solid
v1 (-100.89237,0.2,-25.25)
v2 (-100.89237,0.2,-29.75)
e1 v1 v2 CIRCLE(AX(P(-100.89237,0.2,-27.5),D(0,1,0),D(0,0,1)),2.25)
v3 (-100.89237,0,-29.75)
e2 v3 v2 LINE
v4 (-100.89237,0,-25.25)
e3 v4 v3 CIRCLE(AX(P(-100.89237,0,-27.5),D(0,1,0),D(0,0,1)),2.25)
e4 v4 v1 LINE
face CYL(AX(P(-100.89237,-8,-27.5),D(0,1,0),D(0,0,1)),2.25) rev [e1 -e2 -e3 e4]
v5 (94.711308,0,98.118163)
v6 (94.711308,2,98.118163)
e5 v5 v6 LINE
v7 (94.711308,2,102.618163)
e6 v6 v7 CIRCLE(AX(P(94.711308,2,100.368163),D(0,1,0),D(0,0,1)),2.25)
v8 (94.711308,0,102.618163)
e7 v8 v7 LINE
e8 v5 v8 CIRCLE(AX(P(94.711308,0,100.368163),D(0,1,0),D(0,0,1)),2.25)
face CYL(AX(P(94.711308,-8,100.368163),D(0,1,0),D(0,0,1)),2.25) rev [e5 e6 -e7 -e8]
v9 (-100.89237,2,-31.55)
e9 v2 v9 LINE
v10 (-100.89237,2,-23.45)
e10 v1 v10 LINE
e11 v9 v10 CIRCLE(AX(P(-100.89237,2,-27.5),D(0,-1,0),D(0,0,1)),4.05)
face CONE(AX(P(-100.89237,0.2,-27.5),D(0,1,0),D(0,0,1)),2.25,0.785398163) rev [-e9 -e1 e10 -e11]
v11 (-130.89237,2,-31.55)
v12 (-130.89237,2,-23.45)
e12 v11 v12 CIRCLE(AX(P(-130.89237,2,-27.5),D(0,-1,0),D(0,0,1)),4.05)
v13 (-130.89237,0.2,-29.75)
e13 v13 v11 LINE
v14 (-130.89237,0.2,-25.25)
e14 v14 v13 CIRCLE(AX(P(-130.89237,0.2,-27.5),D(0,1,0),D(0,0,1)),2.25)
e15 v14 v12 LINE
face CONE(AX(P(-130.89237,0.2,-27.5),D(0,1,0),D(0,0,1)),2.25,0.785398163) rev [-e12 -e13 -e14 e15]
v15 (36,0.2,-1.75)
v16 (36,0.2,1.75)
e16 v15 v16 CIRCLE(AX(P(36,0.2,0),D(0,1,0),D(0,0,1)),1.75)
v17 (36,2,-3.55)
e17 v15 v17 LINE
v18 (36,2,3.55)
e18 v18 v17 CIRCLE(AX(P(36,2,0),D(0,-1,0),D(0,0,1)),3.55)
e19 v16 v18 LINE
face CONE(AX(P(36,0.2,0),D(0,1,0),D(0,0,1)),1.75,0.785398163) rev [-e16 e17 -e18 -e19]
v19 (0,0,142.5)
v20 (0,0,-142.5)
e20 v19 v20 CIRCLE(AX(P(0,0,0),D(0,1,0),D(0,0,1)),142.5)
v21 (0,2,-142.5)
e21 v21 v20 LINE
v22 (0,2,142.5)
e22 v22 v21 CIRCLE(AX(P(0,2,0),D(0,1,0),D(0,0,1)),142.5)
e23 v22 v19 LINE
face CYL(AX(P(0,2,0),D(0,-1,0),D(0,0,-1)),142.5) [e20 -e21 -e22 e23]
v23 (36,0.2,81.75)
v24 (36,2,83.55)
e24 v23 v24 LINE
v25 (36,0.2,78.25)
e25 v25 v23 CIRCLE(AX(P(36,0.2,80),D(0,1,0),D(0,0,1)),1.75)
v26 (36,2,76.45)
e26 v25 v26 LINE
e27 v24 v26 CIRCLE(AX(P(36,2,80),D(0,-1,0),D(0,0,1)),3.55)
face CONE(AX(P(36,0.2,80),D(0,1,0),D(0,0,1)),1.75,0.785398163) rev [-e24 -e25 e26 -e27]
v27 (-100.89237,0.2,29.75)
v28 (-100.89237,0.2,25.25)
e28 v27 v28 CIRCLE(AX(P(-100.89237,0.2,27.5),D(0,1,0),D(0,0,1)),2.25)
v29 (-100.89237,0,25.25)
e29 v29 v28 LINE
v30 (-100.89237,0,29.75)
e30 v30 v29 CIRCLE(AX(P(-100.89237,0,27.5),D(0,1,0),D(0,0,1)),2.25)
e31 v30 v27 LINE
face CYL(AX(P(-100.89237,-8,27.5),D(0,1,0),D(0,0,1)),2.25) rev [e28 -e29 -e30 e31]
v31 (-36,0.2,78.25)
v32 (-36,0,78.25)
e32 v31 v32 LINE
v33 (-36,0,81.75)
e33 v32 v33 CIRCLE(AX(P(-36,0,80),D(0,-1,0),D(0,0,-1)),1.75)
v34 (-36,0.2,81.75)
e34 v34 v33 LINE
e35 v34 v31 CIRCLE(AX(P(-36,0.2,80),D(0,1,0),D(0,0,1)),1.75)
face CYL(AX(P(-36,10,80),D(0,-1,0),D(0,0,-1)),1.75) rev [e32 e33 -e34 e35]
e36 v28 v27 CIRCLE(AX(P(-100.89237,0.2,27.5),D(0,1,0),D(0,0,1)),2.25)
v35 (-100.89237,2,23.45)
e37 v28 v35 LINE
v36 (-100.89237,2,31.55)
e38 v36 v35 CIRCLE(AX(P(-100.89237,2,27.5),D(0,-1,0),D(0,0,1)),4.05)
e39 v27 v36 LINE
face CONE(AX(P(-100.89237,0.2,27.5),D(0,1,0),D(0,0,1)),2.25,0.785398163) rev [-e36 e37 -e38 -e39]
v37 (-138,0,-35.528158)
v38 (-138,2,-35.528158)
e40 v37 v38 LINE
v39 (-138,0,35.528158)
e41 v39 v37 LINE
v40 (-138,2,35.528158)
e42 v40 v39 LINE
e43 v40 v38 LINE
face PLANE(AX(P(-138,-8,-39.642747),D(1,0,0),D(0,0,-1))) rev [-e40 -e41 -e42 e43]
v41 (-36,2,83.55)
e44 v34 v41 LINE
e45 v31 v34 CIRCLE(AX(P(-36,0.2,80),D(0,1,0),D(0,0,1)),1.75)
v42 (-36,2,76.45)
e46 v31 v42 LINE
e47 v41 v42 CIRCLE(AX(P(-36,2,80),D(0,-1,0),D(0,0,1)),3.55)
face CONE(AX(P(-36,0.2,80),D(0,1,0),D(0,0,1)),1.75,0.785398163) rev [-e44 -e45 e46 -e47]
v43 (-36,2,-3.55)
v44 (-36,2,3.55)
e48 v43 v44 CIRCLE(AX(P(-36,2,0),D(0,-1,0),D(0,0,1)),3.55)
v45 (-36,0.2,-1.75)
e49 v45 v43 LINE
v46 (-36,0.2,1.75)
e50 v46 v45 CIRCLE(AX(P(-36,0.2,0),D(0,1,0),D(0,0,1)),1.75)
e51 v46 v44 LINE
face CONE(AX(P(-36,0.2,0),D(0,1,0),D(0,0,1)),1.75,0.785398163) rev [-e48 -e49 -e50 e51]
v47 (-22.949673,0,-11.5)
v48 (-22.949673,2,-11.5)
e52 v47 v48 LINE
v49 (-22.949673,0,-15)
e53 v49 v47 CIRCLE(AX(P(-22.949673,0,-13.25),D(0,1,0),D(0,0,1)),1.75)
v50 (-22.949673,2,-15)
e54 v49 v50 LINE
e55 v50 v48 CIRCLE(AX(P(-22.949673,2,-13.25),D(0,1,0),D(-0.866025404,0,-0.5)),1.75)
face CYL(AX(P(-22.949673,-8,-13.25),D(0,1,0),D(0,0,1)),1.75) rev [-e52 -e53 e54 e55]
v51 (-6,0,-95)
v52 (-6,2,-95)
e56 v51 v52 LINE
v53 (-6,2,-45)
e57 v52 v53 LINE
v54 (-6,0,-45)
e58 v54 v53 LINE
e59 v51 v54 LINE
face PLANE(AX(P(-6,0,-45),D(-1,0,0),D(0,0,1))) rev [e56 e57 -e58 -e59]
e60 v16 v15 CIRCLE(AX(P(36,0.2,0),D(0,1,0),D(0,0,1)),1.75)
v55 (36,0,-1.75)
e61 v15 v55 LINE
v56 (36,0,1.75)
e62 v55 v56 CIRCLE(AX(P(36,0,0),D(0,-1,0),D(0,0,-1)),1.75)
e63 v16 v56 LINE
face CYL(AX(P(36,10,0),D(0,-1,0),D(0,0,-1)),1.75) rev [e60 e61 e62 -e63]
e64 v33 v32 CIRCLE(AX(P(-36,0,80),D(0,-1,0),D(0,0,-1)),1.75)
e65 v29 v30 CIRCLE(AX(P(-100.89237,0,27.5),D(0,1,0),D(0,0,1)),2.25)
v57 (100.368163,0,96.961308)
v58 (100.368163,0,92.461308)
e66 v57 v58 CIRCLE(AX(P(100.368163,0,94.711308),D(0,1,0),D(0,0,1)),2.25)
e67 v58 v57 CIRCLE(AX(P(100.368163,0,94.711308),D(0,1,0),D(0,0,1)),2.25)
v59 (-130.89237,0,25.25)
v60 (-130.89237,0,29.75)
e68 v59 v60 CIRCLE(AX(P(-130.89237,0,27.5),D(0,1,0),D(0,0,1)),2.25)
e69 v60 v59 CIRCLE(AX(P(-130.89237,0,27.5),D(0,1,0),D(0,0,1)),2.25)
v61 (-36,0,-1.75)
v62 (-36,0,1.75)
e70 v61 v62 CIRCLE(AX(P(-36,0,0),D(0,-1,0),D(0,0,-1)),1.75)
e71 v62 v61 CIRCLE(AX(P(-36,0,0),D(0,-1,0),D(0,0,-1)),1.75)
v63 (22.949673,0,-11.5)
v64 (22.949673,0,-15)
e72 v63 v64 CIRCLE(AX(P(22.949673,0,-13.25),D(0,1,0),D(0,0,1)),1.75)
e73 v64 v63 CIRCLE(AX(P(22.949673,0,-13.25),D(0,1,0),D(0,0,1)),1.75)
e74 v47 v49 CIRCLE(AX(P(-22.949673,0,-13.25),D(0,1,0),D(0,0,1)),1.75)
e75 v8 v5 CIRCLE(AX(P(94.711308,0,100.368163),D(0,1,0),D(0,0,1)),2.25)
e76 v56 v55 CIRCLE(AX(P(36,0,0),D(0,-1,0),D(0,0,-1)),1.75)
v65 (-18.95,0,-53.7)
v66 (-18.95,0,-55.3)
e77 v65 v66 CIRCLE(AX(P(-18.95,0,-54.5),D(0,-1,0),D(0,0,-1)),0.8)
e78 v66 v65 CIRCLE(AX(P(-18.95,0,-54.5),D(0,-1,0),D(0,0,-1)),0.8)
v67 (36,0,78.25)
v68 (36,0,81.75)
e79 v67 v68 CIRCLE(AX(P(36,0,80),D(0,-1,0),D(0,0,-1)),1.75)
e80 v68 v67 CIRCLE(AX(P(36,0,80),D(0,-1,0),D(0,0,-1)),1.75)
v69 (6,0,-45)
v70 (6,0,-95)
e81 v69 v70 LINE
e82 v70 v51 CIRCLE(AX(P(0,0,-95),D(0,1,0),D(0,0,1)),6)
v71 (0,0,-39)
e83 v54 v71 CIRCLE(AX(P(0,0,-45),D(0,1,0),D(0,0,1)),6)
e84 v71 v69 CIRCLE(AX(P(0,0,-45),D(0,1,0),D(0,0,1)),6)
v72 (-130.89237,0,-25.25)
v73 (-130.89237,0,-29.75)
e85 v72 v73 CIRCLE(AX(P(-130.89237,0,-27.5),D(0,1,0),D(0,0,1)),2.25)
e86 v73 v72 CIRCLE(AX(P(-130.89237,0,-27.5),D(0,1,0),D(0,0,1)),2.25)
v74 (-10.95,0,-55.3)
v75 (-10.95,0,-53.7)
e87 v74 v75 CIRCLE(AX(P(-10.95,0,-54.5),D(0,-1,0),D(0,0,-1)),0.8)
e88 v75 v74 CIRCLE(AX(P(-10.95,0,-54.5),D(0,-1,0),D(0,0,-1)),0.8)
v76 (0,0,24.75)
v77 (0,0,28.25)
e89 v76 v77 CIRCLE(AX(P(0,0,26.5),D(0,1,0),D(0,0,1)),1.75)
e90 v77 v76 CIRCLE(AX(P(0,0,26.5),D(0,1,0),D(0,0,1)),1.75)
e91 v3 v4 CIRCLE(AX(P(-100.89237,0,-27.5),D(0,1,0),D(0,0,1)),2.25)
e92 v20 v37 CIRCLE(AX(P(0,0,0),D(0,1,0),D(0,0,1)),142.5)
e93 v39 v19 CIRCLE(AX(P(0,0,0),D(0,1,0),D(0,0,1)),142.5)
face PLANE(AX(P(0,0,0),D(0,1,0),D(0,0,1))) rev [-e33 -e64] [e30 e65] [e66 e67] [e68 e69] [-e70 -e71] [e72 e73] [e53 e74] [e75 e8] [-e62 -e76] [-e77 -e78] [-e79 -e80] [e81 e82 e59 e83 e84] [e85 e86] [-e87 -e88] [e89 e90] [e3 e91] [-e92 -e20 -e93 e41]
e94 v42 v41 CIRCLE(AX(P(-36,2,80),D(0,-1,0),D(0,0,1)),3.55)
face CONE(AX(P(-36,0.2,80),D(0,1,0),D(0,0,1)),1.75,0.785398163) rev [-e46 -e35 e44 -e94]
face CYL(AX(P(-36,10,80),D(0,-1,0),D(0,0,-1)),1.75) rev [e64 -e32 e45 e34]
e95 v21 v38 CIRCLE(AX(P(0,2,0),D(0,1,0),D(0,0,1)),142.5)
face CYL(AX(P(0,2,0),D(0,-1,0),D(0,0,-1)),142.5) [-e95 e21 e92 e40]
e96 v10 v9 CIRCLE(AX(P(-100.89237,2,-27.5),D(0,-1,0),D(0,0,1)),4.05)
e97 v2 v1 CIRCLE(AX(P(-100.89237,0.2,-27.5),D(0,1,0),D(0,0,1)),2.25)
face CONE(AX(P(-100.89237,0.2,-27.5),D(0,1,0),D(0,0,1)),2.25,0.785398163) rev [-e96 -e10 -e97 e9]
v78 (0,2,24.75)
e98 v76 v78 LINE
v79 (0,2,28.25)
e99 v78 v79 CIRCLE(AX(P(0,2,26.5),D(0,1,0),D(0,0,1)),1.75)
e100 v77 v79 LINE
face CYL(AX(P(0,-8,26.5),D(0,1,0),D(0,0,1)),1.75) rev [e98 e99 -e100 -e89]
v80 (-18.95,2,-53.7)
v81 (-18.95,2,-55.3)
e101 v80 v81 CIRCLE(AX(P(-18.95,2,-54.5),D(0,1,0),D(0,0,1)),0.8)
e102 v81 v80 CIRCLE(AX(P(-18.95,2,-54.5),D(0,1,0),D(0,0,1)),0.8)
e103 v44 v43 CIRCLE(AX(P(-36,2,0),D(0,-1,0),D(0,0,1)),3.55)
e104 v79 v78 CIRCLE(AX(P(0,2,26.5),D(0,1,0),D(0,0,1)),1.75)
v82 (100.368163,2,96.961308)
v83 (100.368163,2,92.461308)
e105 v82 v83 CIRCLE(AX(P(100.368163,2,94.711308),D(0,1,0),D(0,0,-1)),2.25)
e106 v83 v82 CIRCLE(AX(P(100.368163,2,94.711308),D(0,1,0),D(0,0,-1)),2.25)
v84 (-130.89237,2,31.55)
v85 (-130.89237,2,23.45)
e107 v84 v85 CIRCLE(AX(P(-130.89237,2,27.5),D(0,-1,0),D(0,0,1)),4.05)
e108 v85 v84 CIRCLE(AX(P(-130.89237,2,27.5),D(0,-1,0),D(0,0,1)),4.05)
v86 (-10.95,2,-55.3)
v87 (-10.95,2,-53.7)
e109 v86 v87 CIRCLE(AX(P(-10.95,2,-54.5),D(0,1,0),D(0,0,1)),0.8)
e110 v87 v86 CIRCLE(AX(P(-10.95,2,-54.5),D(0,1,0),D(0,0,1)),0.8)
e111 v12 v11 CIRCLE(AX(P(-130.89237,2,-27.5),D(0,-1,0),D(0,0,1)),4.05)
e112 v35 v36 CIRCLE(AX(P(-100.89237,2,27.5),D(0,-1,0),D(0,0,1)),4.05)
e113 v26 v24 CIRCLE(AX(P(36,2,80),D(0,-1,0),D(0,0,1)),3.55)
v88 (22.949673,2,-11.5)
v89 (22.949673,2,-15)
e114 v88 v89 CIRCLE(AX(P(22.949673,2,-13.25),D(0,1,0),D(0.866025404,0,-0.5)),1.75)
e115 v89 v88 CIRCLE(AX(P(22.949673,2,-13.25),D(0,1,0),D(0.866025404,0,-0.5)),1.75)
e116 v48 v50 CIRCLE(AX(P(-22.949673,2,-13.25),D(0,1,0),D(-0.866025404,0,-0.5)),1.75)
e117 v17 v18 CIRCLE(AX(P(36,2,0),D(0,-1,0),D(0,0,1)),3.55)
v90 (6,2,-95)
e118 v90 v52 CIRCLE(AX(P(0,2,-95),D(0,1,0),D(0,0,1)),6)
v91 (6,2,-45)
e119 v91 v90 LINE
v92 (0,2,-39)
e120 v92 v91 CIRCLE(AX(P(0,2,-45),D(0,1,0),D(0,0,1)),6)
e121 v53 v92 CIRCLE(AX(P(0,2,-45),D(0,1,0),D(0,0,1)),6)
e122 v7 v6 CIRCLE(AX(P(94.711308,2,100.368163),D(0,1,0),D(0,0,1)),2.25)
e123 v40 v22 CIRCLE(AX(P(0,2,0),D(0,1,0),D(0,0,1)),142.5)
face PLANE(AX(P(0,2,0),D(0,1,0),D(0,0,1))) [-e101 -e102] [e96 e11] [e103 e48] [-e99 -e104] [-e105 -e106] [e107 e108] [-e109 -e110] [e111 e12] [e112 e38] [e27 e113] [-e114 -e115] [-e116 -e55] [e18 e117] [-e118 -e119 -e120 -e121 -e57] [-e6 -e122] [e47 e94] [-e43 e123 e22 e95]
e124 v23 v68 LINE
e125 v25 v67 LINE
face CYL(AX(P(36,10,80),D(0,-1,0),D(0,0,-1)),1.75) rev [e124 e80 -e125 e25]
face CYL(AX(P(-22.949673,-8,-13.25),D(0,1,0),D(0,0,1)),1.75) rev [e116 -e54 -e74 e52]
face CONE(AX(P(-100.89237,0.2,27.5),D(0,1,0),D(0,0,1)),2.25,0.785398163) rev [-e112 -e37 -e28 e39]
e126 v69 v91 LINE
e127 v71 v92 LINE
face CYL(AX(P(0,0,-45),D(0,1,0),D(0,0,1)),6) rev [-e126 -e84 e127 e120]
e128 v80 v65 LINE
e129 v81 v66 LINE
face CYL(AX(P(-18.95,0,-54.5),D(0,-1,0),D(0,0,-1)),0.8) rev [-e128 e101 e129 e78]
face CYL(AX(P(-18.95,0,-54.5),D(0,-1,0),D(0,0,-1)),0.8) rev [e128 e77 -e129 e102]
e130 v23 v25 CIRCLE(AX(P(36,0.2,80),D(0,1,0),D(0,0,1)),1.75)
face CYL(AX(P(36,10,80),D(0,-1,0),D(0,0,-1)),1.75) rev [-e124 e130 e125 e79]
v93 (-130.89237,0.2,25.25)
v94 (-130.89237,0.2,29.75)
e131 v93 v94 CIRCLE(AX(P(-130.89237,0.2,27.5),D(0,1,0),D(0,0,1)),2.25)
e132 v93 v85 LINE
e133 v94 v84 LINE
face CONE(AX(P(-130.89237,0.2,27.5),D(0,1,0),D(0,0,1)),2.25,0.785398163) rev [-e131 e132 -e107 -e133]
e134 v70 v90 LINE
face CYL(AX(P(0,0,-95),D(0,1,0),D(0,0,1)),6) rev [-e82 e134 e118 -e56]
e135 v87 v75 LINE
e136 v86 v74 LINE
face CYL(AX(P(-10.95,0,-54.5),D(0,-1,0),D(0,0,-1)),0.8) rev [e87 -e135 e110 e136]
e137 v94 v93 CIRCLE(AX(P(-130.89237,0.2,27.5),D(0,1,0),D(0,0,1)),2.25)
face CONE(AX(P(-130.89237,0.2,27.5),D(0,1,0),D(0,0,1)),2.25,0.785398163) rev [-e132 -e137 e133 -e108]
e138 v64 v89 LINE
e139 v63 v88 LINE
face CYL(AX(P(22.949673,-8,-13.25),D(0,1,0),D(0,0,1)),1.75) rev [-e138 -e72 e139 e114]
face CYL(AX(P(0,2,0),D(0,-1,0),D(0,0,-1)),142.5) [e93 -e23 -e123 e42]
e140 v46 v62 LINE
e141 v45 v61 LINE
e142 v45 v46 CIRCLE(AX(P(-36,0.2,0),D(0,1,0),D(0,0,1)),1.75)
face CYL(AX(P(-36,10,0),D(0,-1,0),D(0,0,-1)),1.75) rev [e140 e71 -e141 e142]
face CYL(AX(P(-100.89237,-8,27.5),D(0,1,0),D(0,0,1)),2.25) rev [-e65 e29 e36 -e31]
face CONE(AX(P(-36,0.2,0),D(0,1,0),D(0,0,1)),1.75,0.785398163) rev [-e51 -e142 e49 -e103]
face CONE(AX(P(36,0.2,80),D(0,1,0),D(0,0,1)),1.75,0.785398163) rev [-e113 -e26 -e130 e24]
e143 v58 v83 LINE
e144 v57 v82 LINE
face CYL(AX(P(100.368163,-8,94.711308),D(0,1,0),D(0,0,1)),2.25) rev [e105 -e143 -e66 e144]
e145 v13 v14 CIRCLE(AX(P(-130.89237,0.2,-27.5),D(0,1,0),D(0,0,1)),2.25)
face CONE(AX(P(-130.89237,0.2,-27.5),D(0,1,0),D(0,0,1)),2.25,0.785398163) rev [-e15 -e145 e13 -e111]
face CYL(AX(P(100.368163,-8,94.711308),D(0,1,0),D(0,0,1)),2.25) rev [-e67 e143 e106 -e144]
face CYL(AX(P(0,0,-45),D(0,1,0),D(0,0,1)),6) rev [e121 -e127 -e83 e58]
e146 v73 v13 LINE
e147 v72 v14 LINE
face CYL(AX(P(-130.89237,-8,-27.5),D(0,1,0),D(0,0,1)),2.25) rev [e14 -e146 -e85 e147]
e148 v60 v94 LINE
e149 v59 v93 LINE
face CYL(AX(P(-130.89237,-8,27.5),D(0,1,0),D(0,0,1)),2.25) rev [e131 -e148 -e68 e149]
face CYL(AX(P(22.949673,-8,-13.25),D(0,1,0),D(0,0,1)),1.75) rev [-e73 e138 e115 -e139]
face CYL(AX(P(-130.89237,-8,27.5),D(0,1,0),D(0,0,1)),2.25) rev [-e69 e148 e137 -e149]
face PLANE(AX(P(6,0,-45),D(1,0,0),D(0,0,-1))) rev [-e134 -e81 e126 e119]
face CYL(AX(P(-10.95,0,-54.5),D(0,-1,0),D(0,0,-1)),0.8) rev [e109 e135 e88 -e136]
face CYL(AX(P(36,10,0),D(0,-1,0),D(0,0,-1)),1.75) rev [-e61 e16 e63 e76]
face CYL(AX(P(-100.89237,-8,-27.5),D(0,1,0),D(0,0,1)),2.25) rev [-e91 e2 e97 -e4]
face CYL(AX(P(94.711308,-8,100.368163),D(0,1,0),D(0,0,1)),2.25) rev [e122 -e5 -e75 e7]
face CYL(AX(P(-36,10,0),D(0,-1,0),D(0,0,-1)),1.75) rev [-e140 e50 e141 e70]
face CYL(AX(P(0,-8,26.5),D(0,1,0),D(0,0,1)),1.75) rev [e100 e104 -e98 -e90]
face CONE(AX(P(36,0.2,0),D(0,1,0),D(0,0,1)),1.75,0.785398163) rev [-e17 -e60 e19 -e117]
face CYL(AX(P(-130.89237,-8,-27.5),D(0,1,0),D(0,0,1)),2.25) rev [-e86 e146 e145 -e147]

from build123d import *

# Parameters (mm, degrees)
SKETCH1_R             = 142.5
BOSS_EXTRUDE1_DEPTH   = 2
SKETCH3_R             = 1.75
CUT_EXTRUDE1_DEPTH    = 10
CIRPATTERN1_COUNT     = 3
SKETCH5_R             = 2.25
CUT_EXTRUDE2_DEPTH    = 10
CUT_EXTRUDE3_DEPTH    = 202.5353567
SKETCH7_R             = 1.75
CUT_EXTRUDE4_DEPTH    = 10
CHAMFER1_SIZE         = 1.8
CHAMFER2_SIZE         = 1.8
M2_TAPPED_HOLE1_D     = 1.6
M2_TAPPED_HOLE1_DEPTH = 5.2
M2_TAPPED_HOLE1_TIP   = 0.480688495
SKETCH9_W             = 15.607073654
SKETCH9_H             = 79.285494628
CUT_EXTRUDE5_DEPTH    = 10


with BuildPart() as part:
    # Sketch1 → Boss-Extrude1 (new body)
    with BuildSketch(Plane(origin=(0, 0, 0), x_dir=(1, 0, 0), z_dir=(0, 1, 0))):
        with Locations(Location((0, 0, 0), (0, 0, 270))):
            Circle(SKETCH1_R)
    extrude(amount=BOSS_EXTRUDE1_DEPTH)

    # Sketch3 → Cut-Extrude1 (cut)
    with BuildSketch(Plane(origin=(0, 2, 0), x_dir=(1, 0, 0), z_dir=(0, 1, 0))):
        with Locations(Location((0, -26.5, 0), (0, 0, 270))):
            Circle(SKETCH3_R)
    cut_extrude1 = extrude(amount=-CUT_EXTRUDE1_DEPTH, mode=Mode.SUBTRACT)

    # CirPattern1: Cut-Extrude1 ×3 about axis
    cirpattern1_axis = Axis((0, 0, 0), (0, 1, 0))
    for i in range(1, CIRPATTERN1_COUNT):
        add(cut_extrude1.rotate(cirpattern1_axis, i * 360 / CIRPATTERN1_COUNT), mode=Mode.SUBTRACT)

    # Sketch5 → Cut-Extrude2 (cut)
    with BuildSketch(Plane(origin=(0, 2, 0), x_dir=(1, 0, 0), z_dir=(0, 1, 0))):
        with Locations(Location((94.711308368, -100.368162618, 0), (0, 0, 270))):
            Circle(SKETCH5_R)
        with Locations(Location((100.368162618, -94.711308368, 0), (0, 0, 270))):
            Circle(SKETCH5_R)
        with Locations(Location((-130.892369907, 27.5, 0), (0, 0, 270))):
            Circle(SKETCH5_R)
        with Locations(Location((-130.892369907, -27.5, 0), (0, 0, 270))):
            Circle(SKETCH5_R)
        with Locations(Location((-100.892369907, -27.5, 0), (0, 0, 270))):
            Circle(SKETCH5_R)
        with Locations(Location((-100.892369907, 27.5, 0), (0, 0, 270))):
            Circle(SKETCH5_R)
    extrude(amount=-CUT_EXTRUDE2_DEPTH, mode=Mode.SUBTRACT)

    # Sketch6 → Cut-Extrude3 (cut, through all)
    with BuildSketch(Plane(origin=(0, 2, 0), x_dir=(1, 0, 0), z_dir=(0, 1, 0))):
        with BuildLine():
            Line((-6, 45), (-6, 95))
            ThreePointArc((-6, 95), (0, 101), (6, 95))
            Line((6, 95), (6, 45))
            ThreePointArc((6, 45), (0, 39), (-6, 45))
        make_face()
    extrude(amount=-CUT_EXTRUDE3_DEPTH, mode=Mode.SUBTRACT)

    # Sketch7 → Cut-Extrude4 (cut)
    with BuildSketch(Plane.XZ):
        with Locations(Location((36, 0, 0), (0, 0, 270))):
            Circle(SKETCH7_R)
        with Locations(Location((-36, 0, 0), (0, 0, 270))):
            Circle(SKETCH7_R)
        with Locations(Location((-36, 80, 0), (0, 0, 270))):
            Circle(SKETCH7_R)
        with Locations(Location((36, 80, 0), (0, 0, 270))):
            Circle(SKETCH7_R)
    extrude(amount=-CUT_EXTRUDE4_DEPTH, mode=Mode.SUBTRACT)

    # Chamfer1
    chamfer1_edges = [part.edges().sort_by_distance(p)[0] for p in [
        (36, 2, 1.75),
        (-36, 2, 1.75),
        (-36, 2, 81.75),
        (36, 2, 81.75),
    ]]
    chamfer(chamfer1_edges, length=CHAMFER1_SIZE)

    # Chamfer2
    chamfer2_edges = [part.edges().sort_by_distance(p)[0] for p in [
        (-130.892369907, 2, -29.75),
        (-130.892369907, 2, 25.25),
        (-100.892369907, 2, 25.25),
        (-100.892369907, 2, -29.75),
    ]]
    chamfer(chamfer2_edges, length=CHAMFER2_SIZE)

    # M2 Tapped Hole1
    with Locations(Plane(origin=(-10.95, 0, -54.5), x_dir=(0, 0, -1), z_dir=(0, -1, 0))):
        with Locations((0, 0), (0, -8)):
            Hole(M2_TAPPED_HOLE1_D / 2, depth=M2_TAPPED_HOLE1_DEPTH)
            with Locations((0, 0, -(M2_TAPPED_HOLE1_DEPTH + M2_TAPPED_HOLE1_TIP / 2))):  # 118° drill point
                Cone(0, M2_TAPPED_HOLE1_D / 2, M2_TAPPED_HOLE1_TIP, mode=Mode.SUBTRACT)

    # Sketch9 → Cut-Extrude5 (cut)
    with BuildSketch(Plane(origin=(0, 2, 0), x_dir=(1, 0, 0), z_dir=(0, 1, 0))):
        with Locations((-145.803536827, 0)):
            Rectangle(SKETCH9_W, SKETCH9_H)
    extrude(amount=-CUT_EXTRUDE5_DEPTH, mode=Mode.SUBTRACT)


solid = part.part
